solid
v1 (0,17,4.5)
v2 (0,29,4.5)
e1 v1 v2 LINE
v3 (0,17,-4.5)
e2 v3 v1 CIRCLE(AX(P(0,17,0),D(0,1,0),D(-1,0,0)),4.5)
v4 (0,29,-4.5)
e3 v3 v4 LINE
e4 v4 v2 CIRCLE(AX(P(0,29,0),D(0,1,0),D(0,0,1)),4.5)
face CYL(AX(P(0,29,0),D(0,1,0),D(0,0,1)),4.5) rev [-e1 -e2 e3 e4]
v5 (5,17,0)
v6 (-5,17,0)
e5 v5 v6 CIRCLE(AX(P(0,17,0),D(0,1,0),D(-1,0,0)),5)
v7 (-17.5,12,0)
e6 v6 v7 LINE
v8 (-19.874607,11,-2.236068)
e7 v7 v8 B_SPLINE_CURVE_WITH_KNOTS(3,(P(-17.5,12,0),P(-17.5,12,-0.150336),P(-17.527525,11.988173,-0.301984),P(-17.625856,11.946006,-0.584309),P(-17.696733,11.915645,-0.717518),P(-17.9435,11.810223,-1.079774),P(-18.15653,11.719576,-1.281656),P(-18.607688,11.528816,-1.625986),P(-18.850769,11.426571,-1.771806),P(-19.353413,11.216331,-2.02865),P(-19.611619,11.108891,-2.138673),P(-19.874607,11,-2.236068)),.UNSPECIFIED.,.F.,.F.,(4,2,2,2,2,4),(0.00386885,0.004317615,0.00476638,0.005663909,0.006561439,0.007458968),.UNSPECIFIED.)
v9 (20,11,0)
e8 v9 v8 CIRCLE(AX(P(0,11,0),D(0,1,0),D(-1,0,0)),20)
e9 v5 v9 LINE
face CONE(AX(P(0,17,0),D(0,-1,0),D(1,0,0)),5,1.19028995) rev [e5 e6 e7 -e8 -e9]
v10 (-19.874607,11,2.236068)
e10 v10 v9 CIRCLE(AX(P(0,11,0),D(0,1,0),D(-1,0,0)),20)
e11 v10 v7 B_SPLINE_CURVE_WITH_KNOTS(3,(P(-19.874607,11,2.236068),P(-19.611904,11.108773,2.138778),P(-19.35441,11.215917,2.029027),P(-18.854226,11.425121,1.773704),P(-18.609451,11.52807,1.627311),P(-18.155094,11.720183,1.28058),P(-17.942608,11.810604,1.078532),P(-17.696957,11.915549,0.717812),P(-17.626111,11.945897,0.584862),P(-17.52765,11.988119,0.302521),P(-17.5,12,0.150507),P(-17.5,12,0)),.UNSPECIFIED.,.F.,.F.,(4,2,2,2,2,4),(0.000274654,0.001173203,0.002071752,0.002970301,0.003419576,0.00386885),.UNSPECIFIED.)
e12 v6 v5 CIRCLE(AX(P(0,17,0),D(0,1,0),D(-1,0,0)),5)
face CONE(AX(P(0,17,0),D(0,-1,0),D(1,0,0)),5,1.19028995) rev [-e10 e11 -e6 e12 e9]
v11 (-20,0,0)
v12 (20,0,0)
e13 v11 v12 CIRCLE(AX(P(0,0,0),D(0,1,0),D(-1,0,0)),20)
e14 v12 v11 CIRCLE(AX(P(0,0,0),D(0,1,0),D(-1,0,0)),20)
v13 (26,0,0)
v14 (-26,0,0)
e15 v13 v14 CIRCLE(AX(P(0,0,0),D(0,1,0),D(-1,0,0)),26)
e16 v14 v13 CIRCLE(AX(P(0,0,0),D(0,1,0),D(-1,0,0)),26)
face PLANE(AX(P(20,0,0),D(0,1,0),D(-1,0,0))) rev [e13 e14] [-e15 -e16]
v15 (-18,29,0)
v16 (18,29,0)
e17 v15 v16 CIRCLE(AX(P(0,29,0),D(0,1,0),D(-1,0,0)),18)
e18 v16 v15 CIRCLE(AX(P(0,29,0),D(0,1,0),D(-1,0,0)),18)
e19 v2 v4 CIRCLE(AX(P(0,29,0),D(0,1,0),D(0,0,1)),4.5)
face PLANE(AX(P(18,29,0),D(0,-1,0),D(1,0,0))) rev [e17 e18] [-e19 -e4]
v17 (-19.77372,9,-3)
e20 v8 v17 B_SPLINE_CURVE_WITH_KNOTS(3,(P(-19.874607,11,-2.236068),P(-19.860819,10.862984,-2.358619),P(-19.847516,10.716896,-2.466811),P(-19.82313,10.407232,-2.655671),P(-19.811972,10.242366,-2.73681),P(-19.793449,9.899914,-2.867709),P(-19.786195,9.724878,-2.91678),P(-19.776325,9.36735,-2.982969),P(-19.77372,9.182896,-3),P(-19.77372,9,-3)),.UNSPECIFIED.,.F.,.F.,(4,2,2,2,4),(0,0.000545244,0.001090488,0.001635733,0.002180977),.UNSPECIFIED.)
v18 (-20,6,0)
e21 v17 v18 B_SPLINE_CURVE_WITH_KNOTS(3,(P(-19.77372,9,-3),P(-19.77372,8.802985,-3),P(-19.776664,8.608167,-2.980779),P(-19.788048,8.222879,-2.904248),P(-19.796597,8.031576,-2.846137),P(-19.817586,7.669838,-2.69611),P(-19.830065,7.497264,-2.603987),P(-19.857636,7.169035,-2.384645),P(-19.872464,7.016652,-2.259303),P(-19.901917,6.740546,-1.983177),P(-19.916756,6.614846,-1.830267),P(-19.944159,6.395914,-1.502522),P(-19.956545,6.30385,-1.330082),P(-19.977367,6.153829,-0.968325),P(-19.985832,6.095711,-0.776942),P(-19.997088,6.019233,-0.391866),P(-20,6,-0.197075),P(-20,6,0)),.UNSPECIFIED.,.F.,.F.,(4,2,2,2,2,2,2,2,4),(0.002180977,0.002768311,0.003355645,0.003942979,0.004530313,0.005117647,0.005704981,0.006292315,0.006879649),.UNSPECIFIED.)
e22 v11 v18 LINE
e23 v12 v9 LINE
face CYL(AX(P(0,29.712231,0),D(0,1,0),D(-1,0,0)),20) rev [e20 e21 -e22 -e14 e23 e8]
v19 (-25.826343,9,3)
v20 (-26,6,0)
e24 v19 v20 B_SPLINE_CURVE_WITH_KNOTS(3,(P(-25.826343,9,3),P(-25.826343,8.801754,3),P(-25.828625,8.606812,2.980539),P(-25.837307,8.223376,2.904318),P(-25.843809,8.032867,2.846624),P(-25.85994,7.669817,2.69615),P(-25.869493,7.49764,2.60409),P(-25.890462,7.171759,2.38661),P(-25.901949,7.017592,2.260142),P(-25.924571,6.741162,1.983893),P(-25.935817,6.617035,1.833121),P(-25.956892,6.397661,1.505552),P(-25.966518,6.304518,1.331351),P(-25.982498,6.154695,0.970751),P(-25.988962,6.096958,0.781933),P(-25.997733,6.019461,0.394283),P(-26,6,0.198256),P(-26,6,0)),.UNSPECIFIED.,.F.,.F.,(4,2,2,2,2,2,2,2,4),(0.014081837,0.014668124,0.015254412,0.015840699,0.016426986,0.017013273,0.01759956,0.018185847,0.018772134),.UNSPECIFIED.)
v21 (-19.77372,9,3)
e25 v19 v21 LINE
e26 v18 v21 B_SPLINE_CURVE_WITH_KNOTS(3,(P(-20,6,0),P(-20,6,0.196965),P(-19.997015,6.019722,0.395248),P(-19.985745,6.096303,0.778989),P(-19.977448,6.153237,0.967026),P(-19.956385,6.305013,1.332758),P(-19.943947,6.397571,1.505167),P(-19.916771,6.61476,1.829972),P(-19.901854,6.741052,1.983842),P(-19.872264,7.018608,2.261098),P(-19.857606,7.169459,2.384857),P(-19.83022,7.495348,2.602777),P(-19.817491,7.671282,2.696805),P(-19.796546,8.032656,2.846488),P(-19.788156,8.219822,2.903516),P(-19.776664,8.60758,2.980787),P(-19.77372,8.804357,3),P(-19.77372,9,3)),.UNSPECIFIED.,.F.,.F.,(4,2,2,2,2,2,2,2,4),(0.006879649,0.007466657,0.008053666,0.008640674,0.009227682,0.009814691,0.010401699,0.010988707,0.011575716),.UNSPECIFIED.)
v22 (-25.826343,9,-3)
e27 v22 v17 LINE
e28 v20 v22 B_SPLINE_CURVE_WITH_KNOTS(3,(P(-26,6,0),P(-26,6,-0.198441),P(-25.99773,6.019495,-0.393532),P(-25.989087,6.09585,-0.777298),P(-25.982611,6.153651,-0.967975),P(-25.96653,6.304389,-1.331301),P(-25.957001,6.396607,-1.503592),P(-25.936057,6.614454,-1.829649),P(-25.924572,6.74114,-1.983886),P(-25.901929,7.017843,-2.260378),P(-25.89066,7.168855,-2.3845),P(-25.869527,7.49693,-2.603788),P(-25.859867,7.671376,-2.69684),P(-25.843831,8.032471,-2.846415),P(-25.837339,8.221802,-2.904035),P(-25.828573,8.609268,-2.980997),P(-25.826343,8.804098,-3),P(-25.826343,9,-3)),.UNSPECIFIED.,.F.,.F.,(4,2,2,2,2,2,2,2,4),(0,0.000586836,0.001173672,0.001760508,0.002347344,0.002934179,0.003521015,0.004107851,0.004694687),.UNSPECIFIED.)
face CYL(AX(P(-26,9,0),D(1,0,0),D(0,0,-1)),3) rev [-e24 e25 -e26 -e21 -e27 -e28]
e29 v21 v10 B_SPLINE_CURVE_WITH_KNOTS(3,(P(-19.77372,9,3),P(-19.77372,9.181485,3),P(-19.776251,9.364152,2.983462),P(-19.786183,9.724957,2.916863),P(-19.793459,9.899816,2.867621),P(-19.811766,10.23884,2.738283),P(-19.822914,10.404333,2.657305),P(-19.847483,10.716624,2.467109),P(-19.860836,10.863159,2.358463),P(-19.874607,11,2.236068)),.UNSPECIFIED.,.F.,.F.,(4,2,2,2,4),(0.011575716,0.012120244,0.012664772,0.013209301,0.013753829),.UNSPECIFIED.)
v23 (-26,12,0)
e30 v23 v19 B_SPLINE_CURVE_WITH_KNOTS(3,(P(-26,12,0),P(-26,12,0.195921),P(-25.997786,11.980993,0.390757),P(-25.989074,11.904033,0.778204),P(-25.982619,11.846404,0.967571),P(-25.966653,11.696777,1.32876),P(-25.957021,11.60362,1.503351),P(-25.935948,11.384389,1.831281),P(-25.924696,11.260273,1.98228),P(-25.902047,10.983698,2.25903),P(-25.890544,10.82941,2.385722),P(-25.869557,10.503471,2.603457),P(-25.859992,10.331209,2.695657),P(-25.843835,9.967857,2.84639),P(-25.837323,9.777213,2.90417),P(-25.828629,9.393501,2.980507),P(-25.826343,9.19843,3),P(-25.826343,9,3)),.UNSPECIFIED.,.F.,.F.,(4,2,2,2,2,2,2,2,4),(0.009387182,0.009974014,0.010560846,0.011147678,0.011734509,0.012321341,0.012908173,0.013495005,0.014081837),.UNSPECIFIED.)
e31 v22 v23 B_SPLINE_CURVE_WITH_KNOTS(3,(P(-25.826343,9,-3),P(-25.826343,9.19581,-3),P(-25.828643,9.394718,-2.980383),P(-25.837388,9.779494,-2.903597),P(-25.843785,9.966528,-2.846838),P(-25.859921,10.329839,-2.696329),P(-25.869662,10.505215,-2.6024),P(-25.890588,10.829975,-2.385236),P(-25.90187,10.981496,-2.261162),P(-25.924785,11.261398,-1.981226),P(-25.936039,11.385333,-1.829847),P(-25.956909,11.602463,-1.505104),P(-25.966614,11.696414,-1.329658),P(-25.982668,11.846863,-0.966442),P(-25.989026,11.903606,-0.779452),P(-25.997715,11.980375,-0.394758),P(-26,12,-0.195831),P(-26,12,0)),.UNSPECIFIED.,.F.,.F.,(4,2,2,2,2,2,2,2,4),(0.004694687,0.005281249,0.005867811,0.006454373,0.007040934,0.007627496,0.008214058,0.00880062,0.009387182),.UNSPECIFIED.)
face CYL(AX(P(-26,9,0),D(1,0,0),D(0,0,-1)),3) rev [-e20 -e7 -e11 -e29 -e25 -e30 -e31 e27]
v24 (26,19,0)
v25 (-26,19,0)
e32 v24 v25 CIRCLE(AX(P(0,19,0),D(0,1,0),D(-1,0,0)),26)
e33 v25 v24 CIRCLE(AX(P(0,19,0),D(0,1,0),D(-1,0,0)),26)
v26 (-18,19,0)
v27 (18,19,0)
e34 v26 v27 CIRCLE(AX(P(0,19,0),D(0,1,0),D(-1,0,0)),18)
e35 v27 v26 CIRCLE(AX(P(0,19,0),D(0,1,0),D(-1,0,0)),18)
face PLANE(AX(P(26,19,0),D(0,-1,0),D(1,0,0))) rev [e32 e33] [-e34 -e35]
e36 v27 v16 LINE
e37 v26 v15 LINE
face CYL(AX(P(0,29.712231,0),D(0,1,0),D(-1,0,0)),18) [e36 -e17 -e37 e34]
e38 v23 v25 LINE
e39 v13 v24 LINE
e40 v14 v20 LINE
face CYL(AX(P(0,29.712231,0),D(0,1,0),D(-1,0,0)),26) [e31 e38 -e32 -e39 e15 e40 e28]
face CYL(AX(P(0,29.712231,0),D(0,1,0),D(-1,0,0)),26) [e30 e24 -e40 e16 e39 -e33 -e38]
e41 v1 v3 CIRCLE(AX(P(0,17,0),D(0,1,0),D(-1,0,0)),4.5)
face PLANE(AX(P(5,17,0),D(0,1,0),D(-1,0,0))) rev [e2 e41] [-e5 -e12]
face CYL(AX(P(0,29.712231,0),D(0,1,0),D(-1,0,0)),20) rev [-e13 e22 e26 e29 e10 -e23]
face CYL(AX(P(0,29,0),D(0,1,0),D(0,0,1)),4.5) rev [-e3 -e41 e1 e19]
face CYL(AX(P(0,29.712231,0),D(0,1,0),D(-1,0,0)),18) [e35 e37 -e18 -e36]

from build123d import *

# Parameters (mm, degrees)
M10X1_0_TAPPED_HOLE1_D = 9
SKETCH4_R              = 3
CUT_EXTRUDE1_DEPTH     = 47.829477896


with BuildPart() as part:
    # Sketch1 → Revolve1 (revolve)
    with BuildSketch(Plane.XY, mode=Mode.PRIVATE) as revolve1_sk:
        Polygon((20, 0), (26, 0), (26, 19), (18, 19), (18, 29), (0, 29), (0, 17), (5, 17), (20, 11), align=None)
    revolve(revolve1_sk.sketch.rotate(Axis((0, 29.712230849, 0), (0, -1, 0)), 180), axis=Axis((0, 29.712230849, 0), (0, -1, 0)))

    # M10x1.0 Tapped Hole1 (through all)
    with Locations(Plane(origin=(0, 29, 0), x_dir=(1, 0, 0), z_dir=(0, 1, 0))):
        with Locations((0, 0)):
            Hole(M10X1_0_TAPPED_HOLE1_D / 2)

    # Sketch4 → Cut-Extrude1 (cut, through all)
    with BuildSketch(Plane(origin=(0, 0, 0), x_dir=(0, 0, -1), z_dir=(1, 0, 0))):
        with Locations(Location((0, 9, 0), (0, 0, 270.000000001))):
            Circle(SKETCH4_R)
    extrude(amount=-CUT_EXTRUDE1_DEPTH, mode=Mode.SUBTRACT)


solid = part.part
